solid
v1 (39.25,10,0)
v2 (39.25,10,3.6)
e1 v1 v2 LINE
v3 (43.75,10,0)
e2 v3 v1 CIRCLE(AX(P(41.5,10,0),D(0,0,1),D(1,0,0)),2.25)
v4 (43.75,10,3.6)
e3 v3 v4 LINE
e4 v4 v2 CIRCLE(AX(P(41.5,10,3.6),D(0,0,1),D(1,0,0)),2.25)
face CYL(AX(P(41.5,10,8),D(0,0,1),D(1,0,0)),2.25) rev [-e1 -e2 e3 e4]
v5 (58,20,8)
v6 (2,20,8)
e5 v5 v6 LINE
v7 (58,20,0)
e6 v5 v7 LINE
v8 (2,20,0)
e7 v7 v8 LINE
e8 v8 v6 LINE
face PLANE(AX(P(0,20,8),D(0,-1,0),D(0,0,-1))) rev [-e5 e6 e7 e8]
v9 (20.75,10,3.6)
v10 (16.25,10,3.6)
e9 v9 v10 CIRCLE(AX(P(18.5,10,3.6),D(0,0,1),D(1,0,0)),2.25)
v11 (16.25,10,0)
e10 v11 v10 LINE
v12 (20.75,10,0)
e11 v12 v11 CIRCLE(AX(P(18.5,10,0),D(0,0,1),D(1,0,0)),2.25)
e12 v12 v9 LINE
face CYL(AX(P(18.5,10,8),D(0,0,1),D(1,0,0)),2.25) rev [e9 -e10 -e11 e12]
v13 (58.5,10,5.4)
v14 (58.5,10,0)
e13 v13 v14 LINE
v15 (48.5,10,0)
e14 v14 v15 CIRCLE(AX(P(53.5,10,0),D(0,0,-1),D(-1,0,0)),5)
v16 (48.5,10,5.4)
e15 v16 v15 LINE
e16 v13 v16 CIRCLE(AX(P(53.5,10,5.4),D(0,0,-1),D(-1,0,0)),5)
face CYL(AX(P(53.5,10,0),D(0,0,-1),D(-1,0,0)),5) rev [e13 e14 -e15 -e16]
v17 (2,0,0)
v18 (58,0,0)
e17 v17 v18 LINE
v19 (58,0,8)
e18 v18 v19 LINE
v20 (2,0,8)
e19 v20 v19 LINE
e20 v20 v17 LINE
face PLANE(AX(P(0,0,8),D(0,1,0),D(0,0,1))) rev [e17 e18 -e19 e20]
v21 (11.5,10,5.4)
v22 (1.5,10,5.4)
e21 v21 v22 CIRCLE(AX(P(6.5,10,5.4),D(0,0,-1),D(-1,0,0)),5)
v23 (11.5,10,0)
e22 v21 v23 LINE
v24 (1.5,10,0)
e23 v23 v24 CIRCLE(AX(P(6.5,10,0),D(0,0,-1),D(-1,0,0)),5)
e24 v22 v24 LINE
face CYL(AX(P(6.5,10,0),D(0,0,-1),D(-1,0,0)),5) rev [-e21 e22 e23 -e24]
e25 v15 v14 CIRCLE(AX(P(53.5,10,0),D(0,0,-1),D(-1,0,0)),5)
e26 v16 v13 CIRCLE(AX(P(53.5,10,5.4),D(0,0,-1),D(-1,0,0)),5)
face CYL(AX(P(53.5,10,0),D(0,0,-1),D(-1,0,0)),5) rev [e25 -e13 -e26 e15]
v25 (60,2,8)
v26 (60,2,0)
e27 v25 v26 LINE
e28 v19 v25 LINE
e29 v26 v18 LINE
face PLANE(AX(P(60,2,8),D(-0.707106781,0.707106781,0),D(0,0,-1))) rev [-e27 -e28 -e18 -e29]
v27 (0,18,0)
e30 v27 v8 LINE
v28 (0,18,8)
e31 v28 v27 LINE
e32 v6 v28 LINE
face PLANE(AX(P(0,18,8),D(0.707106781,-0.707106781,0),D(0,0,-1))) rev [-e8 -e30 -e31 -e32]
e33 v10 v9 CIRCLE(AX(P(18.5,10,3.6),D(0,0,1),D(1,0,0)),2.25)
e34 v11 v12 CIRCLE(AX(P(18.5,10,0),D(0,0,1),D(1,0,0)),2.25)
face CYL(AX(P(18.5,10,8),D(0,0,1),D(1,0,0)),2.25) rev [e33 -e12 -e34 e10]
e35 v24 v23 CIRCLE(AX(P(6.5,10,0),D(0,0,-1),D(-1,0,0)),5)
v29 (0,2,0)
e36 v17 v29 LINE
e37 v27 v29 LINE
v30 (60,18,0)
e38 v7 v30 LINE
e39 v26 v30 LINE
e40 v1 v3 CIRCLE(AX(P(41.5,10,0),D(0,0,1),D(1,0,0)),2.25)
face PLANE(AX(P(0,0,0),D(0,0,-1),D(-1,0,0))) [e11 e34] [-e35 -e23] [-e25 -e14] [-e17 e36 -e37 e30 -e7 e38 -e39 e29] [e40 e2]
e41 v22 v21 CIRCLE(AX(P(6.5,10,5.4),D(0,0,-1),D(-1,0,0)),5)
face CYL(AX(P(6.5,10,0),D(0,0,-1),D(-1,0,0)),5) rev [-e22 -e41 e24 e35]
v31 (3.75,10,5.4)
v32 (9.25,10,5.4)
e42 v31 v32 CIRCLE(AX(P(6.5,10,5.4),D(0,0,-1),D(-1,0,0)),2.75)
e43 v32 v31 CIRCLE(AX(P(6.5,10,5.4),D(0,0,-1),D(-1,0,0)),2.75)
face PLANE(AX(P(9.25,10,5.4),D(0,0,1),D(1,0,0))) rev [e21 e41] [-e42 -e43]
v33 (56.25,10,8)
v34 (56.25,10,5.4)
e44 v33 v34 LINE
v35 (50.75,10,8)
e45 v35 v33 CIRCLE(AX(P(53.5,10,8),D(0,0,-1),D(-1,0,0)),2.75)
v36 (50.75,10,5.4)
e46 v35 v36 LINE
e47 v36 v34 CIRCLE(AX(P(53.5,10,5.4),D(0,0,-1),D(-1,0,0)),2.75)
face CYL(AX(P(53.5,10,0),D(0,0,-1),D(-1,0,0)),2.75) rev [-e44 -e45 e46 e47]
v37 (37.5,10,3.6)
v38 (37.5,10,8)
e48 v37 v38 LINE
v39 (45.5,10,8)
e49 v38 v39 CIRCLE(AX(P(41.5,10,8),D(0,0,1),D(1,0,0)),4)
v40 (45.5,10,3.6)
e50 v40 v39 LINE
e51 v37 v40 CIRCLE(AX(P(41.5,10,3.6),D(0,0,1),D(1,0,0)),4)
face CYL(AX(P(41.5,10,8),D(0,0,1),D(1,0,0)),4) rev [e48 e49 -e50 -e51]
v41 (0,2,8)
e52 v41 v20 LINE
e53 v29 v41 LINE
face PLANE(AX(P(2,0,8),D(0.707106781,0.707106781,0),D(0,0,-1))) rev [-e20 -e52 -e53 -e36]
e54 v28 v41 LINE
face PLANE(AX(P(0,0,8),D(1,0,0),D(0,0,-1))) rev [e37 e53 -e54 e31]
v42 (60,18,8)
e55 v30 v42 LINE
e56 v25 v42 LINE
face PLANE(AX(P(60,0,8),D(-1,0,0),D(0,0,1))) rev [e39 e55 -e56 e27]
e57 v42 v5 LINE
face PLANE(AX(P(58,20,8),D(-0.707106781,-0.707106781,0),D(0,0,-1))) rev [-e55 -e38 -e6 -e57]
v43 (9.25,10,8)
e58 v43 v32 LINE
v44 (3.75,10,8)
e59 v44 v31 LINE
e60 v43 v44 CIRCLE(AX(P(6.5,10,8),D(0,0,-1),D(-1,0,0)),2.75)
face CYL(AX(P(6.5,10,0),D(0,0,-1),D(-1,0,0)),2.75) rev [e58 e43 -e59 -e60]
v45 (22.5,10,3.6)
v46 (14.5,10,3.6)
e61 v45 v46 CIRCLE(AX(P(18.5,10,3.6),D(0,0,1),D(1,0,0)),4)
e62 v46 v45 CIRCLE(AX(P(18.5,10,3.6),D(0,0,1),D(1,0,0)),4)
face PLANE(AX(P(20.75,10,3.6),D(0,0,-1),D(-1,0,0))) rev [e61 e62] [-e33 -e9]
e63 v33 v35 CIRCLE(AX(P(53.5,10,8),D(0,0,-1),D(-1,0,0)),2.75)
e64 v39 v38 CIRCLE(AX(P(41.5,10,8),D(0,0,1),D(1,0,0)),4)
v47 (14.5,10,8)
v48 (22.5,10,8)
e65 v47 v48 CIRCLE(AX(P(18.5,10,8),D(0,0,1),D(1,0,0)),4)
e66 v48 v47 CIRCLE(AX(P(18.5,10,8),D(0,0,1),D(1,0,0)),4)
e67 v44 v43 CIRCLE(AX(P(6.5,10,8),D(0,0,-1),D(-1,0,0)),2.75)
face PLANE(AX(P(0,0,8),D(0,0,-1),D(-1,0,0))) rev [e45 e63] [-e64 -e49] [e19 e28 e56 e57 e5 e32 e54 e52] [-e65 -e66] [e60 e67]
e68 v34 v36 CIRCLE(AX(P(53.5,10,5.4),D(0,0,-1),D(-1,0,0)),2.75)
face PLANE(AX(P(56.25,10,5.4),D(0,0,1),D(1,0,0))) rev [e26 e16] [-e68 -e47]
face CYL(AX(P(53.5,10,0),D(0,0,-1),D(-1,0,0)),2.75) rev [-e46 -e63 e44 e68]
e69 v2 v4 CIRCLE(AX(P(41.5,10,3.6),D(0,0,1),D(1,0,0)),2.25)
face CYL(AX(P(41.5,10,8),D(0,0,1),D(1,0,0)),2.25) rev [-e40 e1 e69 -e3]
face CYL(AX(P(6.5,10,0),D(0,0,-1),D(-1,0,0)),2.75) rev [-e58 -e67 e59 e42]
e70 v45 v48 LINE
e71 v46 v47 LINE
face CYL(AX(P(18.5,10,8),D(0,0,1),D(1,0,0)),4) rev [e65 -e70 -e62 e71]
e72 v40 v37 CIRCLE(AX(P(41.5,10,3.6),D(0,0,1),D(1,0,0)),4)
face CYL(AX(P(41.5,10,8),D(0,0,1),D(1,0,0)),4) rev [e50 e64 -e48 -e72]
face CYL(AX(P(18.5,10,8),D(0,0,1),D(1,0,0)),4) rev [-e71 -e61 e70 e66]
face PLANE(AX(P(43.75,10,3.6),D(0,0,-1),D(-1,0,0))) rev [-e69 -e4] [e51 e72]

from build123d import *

# Parameters (mm, degrees)
SKETCH1_W                                           = 60
SKETCH1_H                                           = 20
BOSS_EXTRUDE1_DEPTH                                 = 8
CBORE_FOR_M4_HEX_SOCKET_HEAD_CAP_SCREW2_D           = 4.5
CBORE_FOR_M4_HEX_SOCKET_HEAD_CAP_SCREW2_CBORE_D     = 8
CBORE_FOR_M4_HEX_SOCKET_HEAD_CAP_SCREW2_CBORE_DEPTH = 4.4
CBORE_FOR_M5_HEX_SOCKET_HEAD_CAP_SCREW1_D           = 5.5
CBORE_FOR_M5_HEX_SOCKET_HEAD_CAP_SCREW1_CBORE_D     = 10
CBORE_FOR_M5_HEX_SOCKET_HEAD_CAP_SCREW1_CBORE_DEPTH = 5.4
CHAMFER1_SIZE                                       = 2


with BuildPart() as part:
    # Sketch1 → Boss-Extrude1 (new body)
    with BuildSketch(Plane.XY):
        with Locations((30, 10)):
            Rectangle(SKETCH1_W, SKETCH1_H)
    extrude(amount=BOSS_EXTRUDE1_DEPTH)

    # CBORE for M4 Hex Socket Head Cap Screw2 (through all)
    with Locations(Plane.XY.offset(8)):
        with Locations((41.5, 10), (18.5, 10)):
            CounterBoreHole(CBORE_FOR_M4_HEX_SOCKET_HEAD_CAP_SCREW2_D / 2, CBORE_FOR_M4_HEX_SOCKET_HEAD_CAP_SCREW2_CBORE_D / 2, CBORE_FOR_M4_HEX_SOCKET_HEAD_CAP_SCREW2_CBORE_DEPTH)

    # CBORE for M5 Hex Socket Head Cap Screw1 (through all)
    with Locations(Plane(origin=(0, 0, 0), x_dir=(1, 0, 0), z_dir=(0, 0, -1))):
        with Locations((53.5, -10), (6.5, -10)):
            CounterBoreHole(CBORE_FOR_M5_HEX_SOCKET_HEAD_CAP_SCREW1_D / 2, CBORE_FOR_M5_HEX_SOCKET_HEAD_CAP_SCREW1_CBORE_D / 2, CBORE_FOR_M5_HEX_SOCKET_HEAD_CAP_SCREW1_CBORE_DEPTH)

    # Chamfer1
    chamfer1_edges = [part.edges().sort_by_distance(p)[0] for p in [
        (0, 20, 4),
        (60, 20, 4),
        (60, 0, 4),
        (0, 0, 4),
    ]]
    chamfer(chamfer1_edges, length=CHAMFER1_SIZE)


solid = part.part
